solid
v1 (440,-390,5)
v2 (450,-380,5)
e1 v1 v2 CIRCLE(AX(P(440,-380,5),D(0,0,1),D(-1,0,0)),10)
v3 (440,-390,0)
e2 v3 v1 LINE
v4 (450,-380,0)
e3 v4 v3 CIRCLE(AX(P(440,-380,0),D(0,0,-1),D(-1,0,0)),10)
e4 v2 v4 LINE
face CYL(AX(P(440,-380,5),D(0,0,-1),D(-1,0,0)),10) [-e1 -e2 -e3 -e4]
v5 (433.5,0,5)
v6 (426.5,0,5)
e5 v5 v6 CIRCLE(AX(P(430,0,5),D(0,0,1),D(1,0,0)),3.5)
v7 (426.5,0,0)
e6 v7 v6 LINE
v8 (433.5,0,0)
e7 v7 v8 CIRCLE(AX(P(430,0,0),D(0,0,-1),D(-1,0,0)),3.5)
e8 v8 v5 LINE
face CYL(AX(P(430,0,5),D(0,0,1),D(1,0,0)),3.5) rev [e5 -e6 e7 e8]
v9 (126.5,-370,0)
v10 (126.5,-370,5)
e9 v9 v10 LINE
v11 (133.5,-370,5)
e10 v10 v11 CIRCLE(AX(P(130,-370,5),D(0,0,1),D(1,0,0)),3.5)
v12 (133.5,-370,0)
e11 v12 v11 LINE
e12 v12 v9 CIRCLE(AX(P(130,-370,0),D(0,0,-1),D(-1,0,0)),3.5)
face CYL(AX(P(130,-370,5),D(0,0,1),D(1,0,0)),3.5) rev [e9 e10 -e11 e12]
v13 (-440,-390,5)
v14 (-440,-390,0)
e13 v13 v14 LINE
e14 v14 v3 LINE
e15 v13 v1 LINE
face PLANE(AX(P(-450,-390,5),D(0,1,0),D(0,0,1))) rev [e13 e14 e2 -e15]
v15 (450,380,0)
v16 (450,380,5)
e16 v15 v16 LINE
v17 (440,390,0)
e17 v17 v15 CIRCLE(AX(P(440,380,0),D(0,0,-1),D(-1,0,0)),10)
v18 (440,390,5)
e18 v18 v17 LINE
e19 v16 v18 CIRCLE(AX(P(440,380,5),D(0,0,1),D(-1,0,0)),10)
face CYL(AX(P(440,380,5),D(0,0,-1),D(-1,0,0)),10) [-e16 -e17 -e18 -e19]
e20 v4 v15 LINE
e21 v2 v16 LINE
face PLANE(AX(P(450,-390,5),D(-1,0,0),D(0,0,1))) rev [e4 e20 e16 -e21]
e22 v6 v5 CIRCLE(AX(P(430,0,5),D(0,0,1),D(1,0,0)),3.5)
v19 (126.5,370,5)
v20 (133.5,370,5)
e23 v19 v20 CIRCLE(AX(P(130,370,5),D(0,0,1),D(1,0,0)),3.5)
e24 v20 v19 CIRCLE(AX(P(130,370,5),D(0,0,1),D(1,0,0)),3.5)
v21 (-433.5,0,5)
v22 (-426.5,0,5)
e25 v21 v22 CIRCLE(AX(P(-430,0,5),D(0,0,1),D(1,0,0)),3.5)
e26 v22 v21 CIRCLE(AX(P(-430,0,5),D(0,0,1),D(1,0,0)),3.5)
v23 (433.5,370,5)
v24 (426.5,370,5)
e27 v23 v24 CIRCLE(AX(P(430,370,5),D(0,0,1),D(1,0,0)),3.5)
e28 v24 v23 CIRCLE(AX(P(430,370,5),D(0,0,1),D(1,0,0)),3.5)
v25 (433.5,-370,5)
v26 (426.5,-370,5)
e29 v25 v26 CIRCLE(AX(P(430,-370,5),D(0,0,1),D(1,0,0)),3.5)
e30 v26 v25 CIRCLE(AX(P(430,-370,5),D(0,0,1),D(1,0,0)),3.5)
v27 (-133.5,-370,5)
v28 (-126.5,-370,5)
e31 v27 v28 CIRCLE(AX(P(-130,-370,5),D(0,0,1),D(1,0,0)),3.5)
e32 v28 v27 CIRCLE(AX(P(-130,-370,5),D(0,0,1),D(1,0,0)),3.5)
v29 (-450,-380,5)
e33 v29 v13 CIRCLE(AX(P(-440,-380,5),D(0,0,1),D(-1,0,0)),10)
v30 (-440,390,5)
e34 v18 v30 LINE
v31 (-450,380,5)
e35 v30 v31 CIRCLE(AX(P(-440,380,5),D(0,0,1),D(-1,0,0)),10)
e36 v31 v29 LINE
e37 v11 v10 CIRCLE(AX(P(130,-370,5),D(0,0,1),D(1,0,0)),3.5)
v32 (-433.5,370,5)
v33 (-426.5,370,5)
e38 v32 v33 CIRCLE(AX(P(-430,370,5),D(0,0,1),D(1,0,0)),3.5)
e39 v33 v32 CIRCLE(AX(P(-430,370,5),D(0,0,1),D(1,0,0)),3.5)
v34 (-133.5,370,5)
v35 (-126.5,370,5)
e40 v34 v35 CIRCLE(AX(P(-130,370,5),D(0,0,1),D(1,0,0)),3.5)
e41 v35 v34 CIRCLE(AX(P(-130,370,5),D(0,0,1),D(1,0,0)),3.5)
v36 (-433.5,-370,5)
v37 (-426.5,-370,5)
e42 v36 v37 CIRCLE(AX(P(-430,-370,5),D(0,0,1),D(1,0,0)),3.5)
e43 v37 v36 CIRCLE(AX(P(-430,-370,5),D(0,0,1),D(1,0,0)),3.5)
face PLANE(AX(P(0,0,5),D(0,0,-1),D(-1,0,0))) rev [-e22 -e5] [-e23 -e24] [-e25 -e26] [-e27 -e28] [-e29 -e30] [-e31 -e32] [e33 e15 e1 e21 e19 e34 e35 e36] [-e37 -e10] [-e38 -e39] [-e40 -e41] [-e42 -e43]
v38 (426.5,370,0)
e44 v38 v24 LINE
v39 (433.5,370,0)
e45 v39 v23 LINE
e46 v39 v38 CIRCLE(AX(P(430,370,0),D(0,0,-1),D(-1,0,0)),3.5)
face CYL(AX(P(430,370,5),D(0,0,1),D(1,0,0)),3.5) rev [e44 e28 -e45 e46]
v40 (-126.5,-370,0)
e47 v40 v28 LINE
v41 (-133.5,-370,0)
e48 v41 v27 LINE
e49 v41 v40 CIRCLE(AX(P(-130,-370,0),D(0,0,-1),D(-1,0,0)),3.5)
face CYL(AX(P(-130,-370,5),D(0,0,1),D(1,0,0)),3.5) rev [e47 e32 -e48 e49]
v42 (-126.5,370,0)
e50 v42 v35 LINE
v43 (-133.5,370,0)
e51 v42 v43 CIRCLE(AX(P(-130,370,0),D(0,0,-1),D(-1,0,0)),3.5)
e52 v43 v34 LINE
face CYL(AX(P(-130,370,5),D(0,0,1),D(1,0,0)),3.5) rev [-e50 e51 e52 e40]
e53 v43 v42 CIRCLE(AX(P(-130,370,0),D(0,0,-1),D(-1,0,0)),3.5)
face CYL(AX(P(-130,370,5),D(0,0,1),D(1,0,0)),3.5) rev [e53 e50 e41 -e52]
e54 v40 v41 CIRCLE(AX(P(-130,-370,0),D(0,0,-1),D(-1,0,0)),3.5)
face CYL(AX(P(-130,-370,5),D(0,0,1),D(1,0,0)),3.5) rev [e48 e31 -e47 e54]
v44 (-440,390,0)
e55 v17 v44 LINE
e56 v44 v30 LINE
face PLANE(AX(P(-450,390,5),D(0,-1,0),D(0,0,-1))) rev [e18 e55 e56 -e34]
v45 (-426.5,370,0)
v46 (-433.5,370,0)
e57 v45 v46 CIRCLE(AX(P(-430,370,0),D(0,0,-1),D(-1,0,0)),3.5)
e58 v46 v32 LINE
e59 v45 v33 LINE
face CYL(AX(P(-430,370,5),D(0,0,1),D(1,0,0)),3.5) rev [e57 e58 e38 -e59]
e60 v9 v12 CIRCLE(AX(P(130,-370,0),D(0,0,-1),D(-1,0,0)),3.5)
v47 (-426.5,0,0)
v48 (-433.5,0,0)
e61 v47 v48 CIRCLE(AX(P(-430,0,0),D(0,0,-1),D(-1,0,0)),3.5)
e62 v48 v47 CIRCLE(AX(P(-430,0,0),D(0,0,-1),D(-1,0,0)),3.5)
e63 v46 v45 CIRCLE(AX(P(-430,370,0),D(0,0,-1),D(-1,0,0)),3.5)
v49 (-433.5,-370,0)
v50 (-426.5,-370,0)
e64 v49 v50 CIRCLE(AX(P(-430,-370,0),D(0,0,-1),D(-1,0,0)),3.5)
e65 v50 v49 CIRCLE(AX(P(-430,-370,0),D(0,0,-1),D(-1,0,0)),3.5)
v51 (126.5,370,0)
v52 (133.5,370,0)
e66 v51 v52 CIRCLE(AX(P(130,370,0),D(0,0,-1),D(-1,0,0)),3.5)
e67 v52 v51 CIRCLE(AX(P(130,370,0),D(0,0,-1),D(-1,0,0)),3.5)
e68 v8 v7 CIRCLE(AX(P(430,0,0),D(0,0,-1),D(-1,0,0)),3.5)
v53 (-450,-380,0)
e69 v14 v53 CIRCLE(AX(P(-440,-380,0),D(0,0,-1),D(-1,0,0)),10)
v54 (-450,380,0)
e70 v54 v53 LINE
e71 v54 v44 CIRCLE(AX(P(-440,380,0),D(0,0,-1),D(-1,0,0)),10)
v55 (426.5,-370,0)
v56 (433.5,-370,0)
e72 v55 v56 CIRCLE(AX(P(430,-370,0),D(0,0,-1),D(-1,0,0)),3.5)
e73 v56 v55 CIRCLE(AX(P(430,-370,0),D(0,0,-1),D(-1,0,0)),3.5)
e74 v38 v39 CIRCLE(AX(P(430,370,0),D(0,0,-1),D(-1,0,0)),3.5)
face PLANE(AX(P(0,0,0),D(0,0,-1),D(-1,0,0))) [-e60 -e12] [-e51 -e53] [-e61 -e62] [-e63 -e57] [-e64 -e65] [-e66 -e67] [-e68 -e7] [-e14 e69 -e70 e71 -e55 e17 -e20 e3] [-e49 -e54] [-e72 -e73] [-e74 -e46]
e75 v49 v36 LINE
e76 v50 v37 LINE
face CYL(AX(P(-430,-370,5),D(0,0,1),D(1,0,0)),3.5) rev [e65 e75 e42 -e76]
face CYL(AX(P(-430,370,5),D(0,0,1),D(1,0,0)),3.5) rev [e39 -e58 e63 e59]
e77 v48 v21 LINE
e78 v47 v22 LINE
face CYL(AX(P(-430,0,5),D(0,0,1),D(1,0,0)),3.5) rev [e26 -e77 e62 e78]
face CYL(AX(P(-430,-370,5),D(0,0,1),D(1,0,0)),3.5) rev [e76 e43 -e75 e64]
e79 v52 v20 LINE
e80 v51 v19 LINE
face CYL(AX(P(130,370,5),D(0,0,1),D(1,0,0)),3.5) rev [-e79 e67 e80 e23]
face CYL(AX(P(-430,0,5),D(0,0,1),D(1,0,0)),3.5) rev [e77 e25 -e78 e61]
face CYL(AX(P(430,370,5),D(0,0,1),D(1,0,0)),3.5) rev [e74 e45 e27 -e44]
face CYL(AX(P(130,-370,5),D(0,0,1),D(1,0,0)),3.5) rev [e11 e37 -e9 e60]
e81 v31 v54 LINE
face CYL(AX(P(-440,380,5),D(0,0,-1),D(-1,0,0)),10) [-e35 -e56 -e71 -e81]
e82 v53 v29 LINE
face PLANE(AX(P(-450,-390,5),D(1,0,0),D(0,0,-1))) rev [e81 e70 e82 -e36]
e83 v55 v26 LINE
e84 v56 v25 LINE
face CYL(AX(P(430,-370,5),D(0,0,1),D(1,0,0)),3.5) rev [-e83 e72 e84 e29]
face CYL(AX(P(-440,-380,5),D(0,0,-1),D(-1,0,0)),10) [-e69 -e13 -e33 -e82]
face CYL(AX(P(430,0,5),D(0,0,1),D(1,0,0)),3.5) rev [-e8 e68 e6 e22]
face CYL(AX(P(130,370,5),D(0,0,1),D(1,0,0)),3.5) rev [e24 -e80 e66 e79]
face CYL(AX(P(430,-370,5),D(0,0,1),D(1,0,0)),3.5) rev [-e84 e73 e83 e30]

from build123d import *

# Parameters (mm, degrees)
SKETCH_1_W                = 900
SKETCH_1_H                = 780
EXTRUDE_1_DEPTH           = 5
HOLE_WIZARD_7_0_7_1_D     = 7
HOLE_WIZARD_7_0_7_1_DEPTH = 27.75
HOLE_WIZARD_7_0_7_1_TIP   = 2.103012167
FILLET_1_R                = 10


with BuildPart() as part:
    # 草图1 → 凸台-拉伸1 (new body)
    with BuildSketch(Plane.XY):
        Rectangle(SKETCH_1_W, SKETCH_1_H)
    extrude(amount=EXTRUDE_1_DEPTH)

    # Ø7.0 (7) 直径孔1
    with Locations(Plane.XY.offset(5)):
        with Locations((-430, 370), (430, 370), (430, -370), (-430, -370), (-430, 0), (430, 0), (-130, 370), (130, 370), (-130, -370), (130, -370)):
            Hole(HOLE_WIZARD_7_0_7_1_D / 2, depth=HOLE_WIZARD_7_0_7_1_DEPTH)
            with Locations((0, 0, -(HOLE_WIZARD_7_0_7_1_DEPTH + HOLE_WIZARD_7_0_7_1_TIP / 2))):  # 118° drill point
                Cone(0, HOLE_WIZARD_7_0_7_1_D / 2, HOLE_WIZARD_7_0_7_1_TIP, mode=Mode.SUBTRACT)

    # 圆角1
    fillet_1_edges = [part.edges().sort_by_distance(p)[0] for p in [
        (450, -390, 2.5),
        (-450, -390, 2.5),
        (-450, 390, 2.5),
        (450, 390, 2.5),
    ]]
    fillet(fillet_1_edges, radius=FILLET_1_R)


solid = part.part
